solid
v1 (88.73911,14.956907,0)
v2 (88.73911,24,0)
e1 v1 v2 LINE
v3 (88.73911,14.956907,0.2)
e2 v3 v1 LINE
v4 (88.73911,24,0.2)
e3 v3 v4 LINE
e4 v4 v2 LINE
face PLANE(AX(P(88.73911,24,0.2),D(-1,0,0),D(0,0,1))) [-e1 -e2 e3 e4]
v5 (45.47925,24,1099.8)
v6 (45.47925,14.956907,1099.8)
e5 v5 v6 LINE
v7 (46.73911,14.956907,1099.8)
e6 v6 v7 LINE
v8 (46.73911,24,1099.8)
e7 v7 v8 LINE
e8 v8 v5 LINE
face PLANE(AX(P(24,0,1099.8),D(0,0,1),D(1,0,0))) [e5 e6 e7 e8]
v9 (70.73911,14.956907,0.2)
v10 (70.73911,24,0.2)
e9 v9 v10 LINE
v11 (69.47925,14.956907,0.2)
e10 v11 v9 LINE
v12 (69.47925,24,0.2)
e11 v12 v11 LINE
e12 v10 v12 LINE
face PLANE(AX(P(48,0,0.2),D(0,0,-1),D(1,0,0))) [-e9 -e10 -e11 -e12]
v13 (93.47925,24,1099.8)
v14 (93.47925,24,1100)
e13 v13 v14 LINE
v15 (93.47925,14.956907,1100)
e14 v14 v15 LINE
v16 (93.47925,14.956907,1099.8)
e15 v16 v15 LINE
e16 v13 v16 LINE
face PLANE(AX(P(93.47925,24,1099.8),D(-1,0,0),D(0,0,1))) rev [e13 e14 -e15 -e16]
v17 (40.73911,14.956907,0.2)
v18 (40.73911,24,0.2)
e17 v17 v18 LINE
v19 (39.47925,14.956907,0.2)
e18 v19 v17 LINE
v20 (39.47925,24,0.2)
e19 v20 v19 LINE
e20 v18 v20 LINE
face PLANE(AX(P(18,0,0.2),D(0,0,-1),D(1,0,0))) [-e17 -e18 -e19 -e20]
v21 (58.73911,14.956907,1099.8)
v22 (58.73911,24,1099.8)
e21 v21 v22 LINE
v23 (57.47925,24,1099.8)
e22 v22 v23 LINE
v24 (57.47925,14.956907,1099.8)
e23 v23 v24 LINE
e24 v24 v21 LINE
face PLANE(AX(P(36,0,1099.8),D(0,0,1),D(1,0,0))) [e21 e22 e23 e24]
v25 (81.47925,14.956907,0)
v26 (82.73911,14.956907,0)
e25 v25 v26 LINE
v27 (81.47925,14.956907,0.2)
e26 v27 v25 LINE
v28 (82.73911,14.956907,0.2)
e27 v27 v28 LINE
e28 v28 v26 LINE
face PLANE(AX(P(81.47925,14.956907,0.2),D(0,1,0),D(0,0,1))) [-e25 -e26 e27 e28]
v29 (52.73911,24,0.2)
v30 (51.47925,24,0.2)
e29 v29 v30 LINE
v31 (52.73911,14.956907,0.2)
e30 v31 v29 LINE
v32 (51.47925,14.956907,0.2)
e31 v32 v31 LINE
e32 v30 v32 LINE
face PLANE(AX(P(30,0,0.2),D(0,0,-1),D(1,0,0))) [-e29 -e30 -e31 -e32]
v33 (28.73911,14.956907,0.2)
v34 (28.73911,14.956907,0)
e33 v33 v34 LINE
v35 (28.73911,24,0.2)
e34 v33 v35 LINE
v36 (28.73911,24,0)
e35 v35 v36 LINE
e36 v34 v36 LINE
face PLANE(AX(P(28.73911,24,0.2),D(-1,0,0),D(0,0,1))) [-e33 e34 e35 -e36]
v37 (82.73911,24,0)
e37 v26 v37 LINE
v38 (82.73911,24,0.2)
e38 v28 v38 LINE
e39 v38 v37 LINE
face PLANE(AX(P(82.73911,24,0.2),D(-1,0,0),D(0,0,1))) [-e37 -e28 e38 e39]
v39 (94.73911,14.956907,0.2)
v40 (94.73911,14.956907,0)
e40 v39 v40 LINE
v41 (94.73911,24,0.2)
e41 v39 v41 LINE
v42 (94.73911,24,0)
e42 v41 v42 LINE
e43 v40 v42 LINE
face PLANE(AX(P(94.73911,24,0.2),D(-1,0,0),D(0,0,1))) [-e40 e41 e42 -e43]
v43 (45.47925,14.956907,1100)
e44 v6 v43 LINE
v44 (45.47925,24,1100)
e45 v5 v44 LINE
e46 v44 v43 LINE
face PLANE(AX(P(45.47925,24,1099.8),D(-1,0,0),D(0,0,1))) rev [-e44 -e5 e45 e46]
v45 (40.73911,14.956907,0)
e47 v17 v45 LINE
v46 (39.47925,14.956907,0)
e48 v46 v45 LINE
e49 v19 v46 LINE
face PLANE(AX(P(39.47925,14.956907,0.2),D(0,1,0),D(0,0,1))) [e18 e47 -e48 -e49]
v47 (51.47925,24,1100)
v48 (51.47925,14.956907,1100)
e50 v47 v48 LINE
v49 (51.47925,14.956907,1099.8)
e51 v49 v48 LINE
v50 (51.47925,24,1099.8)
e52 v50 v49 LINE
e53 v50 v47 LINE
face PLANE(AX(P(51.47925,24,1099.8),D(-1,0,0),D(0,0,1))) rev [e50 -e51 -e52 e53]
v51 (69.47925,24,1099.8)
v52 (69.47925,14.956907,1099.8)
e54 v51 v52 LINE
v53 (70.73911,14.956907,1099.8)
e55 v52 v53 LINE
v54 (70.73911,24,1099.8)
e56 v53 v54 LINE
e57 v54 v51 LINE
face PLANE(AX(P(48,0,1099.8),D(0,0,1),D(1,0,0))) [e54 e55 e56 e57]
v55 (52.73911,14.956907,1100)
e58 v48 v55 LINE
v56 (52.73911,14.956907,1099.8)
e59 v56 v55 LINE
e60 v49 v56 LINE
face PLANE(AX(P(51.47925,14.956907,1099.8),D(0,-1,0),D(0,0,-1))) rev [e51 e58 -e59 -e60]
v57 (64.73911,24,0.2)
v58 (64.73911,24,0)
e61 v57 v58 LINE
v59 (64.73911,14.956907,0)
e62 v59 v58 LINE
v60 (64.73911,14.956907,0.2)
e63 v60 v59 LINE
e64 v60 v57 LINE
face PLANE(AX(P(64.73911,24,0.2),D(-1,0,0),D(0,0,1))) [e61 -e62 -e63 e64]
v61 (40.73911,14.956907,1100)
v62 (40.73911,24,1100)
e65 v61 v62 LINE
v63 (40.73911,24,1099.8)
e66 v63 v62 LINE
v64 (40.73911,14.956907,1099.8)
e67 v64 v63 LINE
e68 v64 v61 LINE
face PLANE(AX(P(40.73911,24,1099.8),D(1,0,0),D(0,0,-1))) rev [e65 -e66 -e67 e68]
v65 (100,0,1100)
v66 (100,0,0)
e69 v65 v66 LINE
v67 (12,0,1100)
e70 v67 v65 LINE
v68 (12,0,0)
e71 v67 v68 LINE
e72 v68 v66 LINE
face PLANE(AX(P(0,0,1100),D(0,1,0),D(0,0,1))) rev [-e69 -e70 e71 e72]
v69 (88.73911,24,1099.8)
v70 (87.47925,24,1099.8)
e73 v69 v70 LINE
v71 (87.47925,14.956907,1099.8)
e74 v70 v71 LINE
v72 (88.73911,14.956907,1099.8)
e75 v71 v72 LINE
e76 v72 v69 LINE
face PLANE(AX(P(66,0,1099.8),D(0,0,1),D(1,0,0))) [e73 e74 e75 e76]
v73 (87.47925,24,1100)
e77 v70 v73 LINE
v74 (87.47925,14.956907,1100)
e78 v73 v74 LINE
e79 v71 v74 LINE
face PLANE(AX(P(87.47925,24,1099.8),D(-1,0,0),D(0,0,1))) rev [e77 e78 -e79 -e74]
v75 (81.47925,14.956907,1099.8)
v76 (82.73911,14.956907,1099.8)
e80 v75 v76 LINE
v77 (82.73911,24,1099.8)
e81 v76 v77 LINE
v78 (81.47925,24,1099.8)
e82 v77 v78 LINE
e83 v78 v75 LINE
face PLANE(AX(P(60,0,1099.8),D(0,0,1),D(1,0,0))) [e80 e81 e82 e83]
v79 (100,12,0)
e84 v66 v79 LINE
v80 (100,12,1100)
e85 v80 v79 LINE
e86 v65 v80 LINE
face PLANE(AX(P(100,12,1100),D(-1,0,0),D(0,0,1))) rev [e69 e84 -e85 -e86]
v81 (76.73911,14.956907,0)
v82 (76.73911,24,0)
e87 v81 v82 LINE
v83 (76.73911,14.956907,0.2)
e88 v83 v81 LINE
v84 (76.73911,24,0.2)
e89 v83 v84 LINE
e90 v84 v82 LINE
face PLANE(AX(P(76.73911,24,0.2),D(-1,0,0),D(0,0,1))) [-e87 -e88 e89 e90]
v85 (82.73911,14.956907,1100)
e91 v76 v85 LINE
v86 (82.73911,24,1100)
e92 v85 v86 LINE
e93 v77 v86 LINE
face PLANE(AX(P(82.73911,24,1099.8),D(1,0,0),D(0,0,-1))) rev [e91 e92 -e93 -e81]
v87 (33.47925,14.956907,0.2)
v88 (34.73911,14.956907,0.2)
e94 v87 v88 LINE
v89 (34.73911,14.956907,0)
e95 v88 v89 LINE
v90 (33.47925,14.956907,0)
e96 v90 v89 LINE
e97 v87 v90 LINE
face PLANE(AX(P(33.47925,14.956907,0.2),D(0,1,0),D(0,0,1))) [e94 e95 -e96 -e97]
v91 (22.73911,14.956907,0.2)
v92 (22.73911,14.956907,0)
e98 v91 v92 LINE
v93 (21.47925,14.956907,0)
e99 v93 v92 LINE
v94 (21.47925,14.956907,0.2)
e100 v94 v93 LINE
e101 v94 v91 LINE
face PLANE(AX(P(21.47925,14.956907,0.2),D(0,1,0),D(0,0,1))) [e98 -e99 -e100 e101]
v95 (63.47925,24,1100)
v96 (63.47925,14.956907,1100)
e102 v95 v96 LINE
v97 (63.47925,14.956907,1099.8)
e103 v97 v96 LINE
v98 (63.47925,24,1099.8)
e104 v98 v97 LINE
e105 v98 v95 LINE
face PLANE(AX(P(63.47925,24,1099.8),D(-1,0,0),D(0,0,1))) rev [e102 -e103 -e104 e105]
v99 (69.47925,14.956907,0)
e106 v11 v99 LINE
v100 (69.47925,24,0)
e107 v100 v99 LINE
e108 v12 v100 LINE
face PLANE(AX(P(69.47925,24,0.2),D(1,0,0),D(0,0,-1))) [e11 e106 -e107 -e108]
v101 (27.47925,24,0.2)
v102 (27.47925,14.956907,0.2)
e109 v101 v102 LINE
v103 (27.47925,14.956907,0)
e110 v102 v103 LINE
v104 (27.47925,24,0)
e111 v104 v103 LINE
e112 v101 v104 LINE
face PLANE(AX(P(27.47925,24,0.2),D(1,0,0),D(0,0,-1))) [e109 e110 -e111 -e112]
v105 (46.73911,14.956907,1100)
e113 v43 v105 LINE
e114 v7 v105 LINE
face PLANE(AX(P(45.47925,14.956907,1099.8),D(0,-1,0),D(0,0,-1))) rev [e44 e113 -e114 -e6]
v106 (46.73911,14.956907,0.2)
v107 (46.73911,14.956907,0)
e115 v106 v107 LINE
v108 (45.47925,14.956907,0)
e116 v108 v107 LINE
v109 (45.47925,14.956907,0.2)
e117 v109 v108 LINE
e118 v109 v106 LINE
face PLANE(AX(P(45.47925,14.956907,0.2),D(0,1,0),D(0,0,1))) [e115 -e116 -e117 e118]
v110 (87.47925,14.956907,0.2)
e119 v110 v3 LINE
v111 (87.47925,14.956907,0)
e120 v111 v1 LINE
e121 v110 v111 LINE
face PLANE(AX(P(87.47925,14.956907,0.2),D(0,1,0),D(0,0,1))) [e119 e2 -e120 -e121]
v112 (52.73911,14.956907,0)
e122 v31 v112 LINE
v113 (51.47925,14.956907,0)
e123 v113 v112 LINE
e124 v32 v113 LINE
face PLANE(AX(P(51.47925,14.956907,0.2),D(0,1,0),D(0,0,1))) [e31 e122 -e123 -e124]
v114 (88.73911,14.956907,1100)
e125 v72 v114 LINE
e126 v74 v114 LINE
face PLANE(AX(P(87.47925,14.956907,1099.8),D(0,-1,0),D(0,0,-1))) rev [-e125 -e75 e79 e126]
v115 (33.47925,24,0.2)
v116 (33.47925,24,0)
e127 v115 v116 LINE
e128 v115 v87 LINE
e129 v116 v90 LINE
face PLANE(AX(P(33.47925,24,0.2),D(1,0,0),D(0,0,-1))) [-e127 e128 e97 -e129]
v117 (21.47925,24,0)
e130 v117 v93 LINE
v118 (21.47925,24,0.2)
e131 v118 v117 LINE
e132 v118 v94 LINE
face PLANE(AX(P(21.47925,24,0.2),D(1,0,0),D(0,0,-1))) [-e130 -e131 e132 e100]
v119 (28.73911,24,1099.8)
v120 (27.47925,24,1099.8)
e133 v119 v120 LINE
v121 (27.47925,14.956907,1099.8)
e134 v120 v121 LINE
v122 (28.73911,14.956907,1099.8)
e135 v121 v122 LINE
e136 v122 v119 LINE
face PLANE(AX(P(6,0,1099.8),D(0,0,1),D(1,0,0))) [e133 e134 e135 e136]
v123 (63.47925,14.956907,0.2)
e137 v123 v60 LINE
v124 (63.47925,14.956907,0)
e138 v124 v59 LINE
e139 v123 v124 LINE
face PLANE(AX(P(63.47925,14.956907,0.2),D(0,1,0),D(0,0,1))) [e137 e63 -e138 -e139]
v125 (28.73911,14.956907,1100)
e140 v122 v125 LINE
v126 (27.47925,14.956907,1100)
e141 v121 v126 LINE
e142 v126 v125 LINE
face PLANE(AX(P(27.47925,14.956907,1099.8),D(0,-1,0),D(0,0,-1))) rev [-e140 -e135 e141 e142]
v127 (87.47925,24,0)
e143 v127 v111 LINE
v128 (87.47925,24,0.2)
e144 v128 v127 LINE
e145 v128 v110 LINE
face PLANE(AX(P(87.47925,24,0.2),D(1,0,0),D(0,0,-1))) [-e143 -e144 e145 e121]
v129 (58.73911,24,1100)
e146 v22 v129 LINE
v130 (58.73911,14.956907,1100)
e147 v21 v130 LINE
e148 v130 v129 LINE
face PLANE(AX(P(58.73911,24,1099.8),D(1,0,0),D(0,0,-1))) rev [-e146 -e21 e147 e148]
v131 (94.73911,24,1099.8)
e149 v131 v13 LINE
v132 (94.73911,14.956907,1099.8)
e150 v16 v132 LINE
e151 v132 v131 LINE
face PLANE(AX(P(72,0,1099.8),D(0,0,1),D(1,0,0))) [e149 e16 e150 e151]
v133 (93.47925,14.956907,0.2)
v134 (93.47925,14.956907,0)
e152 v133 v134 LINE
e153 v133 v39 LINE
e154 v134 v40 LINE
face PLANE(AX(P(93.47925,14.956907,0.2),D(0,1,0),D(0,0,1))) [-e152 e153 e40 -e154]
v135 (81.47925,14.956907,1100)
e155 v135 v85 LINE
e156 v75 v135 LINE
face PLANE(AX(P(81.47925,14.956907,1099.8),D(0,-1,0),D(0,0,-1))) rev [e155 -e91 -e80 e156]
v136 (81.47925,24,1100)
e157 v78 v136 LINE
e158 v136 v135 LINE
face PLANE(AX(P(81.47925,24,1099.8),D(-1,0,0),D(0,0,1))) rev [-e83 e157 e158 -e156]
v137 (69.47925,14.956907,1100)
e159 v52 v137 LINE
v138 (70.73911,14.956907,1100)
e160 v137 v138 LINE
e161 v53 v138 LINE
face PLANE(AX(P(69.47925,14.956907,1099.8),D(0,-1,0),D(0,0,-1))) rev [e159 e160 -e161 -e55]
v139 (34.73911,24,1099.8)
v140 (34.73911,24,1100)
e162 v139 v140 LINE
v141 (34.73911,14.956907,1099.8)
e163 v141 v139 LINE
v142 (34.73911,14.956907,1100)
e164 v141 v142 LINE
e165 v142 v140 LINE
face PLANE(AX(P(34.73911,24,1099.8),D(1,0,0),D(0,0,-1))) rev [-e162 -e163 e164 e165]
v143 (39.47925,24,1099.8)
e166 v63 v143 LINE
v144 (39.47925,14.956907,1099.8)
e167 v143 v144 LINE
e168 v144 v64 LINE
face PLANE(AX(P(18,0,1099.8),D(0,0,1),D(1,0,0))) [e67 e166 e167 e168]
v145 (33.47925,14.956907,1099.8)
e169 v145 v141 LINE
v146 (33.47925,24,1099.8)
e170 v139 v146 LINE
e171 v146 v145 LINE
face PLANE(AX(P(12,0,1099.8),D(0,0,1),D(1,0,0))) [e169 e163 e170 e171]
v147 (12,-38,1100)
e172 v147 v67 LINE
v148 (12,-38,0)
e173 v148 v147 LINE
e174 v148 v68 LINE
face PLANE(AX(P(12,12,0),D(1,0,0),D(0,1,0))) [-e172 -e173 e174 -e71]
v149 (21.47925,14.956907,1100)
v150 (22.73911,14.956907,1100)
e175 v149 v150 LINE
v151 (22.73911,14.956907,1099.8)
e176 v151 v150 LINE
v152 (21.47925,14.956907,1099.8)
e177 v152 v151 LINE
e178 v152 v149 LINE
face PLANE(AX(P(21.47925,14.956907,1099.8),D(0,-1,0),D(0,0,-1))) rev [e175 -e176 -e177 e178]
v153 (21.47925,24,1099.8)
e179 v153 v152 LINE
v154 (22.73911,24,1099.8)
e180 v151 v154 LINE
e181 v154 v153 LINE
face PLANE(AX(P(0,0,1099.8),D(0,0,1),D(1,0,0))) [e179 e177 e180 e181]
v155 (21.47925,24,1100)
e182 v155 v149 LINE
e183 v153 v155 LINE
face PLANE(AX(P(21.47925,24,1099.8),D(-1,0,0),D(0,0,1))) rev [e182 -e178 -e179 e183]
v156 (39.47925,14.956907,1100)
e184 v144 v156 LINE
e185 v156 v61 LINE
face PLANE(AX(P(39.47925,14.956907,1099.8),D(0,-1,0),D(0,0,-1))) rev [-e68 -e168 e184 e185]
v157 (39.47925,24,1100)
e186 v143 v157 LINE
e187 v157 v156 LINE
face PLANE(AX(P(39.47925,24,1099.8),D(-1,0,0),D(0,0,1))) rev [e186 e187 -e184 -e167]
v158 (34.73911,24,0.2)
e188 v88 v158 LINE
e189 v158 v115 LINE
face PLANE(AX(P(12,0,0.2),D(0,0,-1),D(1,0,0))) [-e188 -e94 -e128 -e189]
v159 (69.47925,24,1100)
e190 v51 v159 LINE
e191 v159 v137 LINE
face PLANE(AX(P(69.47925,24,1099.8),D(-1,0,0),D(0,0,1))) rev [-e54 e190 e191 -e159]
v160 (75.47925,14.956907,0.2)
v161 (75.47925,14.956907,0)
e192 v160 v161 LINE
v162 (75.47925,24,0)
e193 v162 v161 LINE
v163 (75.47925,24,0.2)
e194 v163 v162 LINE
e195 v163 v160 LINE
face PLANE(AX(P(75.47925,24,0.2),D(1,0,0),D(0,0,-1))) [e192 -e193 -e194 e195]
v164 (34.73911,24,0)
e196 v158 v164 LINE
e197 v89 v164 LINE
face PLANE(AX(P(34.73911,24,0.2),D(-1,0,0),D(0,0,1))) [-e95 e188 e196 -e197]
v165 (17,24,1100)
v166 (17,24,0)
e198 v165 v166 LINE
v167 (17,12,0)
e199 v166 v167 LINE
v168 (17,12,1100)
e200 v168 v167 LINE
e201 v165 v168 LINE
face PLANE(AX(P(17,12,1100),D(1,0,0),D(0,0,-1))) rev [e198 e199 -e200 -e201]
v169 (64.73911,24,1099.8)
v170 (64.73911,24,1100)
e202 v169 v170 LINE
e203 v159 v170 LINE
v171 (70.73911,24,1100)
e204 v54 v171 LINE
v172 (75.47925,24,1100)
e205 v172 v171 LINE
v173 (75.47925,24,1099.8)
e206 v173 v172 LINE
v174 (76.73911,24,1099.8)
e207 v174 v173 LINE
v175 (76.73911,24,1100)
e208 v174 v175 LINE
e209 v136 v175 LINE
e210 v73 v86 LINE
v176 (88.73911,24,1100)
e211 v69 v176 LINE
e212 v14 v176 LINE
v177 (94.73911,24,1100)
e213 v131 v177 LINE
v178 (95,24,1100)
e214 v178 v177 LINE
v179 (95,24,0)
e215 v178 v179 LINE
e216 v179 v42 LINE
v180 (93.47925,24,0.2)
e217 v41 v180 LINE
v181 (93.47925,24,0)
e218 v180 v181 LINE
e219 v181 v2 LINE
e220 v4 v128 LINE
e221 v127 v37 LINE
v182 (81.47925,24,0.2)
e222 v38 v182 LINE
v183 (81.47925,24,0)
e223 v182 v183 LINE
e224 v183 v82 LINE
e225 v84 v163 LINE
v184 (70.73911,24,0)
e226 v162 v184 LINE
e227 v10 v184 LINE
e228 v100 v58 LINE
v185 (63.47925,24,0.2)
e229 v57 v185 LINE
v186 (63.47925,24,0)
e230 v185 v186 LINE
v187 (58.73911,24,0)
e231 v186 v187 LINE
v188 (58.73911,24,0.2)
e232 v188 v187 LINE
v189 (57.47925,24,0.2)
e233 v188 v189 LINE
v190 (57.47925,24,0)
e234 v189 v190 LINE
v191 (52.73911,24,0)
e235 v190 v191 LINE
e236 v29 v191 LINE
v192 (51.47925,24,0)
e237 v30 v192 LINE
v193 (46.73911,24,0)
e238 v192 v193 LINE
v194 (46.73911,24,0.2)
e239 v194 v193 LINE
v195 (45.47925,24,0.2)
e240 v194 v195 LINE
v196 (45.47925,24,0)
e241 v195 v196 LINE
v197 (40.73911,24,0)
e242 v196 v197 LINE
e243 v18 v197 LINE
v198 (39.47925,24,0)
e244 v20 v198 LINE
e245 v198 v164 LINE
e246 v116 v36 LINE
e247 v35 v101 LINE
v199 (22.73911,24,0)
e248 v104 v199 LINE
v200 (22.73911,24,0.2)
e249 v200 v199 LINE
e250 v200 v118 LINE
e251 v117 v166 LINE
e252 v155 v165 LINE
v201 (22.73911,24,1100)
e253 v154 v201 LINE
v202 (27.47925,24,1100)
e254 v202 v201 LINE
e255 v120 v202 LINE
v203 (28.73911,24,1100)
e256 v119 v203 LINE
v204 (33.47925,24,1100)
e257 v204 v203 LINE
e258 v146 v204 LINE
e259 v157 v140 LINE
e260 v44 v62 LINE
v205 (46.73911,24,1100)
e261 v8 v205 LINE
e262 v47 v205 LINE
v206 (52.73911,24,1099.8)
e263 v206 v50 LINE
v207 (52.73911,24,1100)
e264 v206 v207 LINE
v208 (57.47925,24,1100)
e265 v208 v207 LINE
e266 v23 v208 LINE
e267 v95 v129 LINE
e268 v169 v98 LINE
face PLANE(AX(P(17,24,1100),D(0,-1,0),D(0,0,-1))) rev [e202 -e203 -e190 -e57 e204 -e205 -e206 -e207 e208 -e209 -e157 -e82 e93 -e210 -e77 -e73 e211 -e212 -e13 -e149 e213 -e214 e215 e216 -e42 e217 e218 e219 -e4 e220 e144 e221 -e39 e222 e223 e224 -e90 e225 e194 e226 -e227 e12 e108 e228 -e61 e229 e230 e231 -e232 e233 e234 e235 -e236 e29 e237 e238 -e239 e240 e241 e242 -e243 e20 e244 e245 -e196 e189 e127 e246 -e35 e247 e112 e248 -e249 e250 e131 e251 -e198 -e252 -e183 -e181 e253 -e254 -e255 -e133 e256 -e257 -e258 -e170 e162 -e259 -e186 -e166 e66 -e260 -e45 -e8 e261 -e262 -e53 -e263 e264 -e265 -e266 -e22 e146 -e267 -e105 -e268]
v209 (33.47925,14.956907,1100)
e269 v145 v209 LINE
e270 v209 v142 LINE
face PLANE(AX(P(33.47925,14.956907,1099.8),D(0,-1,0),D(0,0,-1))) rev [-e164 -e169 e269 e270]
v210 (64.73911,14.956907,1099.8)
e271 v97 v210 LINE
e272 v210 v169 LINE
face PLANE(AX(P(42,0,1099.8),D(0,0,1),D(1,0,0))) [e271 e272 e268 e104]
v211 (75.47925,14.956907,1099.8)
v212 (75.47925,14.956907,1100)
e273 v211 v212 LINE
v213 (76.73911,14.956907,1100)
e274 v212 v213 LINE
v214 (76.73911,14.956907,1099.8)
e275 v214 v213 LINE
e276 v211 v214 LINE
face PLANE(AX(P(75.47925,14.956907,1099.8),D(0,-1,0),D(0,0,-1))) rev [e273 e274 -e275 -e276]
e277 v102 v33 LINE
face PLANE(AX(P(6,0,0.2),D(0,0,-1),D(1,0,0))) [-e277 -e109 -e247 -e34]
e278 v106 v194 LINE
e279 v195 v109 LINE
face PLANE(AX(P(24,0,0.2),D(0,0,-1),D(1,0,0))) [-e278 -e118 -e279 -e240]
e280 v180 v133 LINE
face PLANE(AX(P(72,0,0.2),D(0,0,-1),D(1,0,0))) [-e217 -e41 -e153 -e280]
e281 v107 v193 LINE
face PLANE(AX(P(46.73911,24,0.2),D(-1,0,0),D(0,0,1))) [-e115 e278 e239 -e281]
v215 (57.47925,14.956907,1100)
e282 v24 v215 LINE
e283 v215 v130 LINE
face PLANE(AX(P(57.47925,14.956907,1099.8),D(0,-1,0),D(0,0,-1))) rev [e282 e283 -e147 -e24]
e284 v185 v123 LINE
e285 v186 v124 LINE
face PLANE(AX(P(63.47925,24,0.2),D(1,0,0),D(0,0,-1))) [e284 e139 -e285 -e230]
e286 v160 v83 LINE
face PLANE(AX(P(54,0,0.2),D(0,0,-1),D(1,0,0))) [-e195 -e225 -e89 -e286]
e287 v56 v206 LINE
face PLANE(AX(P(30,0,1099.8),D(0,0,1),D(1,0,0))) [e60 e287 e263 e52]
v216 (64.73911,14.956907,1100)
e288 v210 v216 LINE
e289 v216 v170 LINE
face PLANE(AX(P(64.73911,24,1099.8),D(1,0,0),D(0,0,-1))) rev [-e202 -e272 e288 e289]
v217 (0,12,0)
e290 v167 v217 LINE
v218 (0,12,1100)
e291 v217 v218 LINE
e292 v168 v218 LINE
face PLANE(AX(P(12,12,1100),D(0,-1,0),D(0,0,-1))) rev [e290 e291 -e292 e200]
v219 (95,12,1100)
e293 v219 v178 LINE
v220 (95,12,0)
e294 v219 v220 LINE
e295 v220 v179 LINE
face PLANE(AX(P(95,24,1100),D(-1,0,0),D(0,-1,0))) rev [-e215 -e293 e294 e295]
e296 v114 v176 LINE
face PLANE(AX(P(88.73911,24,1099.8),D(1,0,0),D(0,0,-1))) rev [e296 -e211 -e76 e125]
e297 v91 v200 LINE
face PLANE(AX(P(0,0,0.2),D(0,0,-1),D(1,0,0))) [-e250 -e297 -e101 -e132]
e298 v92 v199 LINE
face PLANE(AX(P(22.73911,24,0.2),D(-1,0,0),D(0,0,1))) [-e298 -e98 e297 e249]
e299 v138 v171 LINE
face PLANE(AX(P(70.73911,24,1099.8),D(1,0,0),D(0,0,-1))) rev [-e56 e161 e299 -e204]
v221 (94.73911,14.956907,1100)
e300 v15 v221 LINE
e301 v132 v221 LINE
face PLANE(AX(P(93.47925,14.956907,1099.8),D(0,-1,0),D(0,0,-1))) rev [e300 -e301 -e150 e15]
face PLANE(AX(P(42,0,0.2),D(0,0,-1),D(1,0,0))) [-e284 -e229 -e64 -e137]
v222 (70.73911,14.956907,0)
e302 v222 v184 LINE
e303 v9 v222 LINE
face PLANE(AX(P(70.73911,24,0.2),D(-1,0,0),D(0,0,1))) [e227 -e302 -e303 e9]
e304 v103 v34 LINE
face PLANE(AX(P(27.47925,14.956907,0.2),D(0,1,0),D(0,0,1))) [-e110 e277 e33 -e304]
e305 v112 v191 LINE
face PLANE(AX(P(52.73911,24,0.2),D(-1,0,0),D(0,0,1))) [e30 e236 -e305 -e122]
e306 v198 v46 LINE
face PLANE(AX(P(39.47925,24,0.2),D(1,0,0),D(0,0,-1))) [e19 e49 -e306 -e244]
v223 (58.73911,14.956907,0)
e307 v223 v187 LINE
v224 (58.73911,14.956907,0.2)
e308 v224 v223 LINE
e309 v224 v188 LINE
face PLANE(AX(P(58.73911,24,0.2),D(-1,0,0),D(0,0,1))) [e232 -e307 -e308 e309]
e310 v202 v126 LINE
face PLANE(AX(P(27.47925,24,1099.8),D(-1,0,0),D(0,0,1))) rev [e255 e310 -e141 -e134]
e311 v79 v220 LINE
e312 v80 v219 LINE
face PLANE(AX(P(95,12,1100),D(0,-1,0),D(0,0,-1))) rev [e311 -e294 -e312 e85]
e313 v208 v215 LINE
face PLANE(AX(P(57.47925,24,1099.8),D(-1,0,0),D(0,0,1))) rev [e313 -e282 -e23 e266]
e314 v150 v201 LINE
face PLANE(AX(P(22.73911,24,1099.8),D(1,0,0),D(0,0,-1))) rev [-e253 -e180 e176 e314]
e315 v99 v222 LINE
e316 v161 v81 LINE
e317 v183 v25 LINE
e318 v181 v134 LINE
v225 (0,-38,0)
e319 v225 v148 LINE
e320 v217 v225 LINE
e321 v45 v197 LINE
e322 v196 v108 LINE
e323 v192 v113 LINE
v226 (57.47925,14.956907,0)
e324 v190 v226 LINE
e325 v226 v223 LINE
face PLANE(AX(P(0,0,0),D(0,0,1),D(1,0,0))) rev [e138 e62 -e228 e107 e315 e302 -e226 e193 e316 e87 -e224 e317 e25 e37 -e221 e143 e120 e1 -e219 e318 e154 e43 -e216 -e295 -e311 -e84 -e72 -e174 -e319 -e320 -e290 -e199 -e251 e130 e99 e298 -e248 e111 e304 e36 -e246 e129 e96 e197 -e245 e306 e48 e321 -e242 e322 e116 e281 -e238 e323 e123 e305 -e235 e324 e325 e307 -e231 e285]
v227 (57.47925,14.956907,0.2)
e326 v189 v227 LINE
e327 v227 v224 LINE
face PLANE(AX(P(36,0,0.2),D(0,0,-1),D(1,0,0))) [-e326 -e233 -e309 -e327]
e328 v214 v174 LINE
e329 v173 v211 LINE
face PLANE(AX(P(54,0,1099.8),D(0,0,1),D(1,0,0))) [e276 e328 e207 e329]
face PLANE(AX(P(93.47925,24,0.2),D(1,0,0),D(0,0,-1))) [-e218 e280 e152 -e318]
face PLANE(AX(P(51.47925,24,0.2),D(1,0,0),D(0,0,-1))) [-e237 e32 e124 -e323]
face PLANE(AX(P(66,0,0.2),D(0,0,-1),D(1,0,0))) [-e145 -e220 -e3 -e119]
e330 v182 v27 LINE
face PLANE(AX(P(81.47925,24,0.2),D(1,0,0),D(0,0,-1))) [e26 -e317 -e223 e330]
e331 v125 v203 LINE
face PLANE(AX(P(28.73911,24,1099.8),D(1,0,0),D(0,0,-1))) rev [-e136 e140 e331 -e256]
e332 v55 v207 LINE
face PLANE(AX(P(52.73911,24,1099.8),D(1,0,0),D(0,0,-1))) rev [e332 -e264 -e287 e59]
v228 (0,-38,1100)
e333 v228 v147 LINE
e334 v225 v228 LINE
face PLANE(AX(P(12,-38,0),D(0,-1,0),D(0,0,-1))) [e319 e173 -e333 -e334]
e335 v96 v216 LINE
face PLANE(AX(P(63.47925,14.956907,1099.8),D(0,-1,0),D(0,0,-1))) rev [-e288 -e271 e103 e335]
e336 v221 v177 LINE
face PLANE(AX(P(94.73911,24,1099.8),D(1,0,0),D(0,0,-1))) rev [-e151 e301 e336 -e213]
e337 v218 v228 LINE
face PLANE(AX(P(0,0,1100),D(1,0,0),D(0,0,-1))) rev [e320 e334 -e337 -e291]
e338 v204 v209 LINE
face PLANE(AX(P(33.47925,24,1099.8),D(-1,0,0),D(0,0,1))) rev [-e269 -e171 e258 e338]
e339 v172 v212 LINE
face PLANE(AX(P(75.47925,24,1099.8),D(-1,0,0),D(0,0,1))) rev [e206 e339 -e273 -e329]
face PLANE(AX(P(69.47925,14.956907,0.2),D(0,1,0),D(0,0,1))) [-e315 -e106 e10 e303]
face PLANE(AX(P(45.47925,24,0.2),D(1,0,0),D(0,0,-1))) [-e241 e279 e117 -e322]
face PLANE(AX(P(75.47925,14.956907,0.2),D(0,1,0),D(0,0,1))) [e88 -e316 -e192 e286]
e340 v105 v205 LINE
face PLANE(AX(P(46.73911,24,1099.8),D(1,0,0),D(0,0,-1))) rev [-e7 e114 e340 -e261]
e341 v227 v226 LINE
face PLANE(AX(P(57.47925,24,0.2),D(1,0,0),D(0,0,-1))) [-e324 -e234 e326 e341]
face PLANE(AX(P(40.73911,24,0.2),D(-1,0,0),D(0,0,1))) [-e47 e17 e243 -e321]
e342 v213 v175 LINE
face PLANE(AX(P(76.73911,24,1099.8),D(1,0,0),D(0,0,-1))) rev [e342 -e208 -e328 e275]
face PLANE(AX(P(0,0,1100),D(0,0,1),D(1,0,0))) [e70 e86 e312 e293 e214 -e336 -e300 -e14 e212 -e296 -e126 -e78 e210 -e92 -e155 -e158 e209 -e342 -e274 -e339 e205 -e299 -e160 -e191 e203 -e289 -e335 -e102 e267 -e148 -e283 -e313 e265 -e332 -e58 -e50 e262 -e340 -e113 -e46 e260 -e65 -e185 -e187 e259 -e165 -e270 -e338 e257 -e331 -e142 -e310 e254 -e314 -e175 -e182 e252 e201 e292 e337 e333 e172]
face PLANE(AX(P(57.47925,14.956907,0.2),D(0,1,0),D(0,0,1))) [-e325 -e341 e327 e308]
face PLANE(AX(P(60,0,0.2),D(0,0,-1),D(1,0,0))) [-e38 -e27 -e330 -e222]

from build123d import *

# Parameters (mm, degrees)
BOSS_EXTRUDE1_DEPTH      = 1100
SKETCH2_W                = 1.259860676
SKETCH2_H                = 9.043092937
CUT_EXTRUDE1_DEPTH       = 0.2
LPATTERN1_COUNT          = 16
LPATTERN1_PITCH          = 6
MIRROR1_COPY_1_SKETCH_W  = 1.259860676
MIRROR1_COPY_1_SKETCH_H  = 9.043092937
MIRROR1_COPY_1_DEPTH     = 0.2
MIRROR1_COPY_2_SKETCH_W  = 1.259860676
MIRROR1_COPY_2_SKETCH_H  = 9.043092937
MIRROR1_COPY_2_DEPTH     = 0.2
MIRROR1_COPY_3_SKETCH_W  = 1.259860676
MIRROR1_COPY_3_SKETCH_H  = 9.043092937
MIRROR1_COPY_3_DEPTH     = 0.2
MIRROR1_COPY_4_SKETCH_W  = 1.259860676
MIRROR1_COPY_4_SKETCH_H  = 9.043092937
MIRROR1_COPY_4_DEPTH     = 0.2
MIRROR1_COPY_5_SKETCH_W  = 1.259860676
MIRROR1_COPY_5_SKETCH_H  = 9.043092937
MIRROR1_COPY_5_DEPTH     = 0.2
MIRROR1_COPY_6_SKETCH_W  = 1.259860676
MIRROR1_COPY_6_SKETCH_H  = 9.043092937
MIRROR1_COPY_6_DEPTH     = 0.2
MIRROR1_COPY_7_SKETCH_W  = 1.259860676
MIRROR1_COPY_7_SKETCH_H  = 9.043092937
MIRROR1_COPY_7_DEPTH     = 0.2
MIRROR1_COPY_8_SKETCH_W  = 1.259860676
MIRROR1_COPY_8_SKETCH_H  = 9.043092937
MIRROR1_COPY_8_DEPTH     = 0.2
MIRROR1_COPY_9_SKETCH_W  = 1.259860676
MIRROR1_COPY_9_SKETCH_H  = 9.043092937
MIRROR1_COPY_9_DEPTH     = 0.2
MIRROR1_COPY_10_SKETCH_W = 1.259860676
MIRROR1_COPY_10_SKETCH_H = 9.043092937
MIRROR1_COPY_10_DEPTH    = 0.2
MIRROR1_COPY_11_SKETCH_W = 1.259860676
MIRROR1_COPY_11_SKETCH_H = 9.043092937
MIRROR1_COPY_11_DEPTH    = 0.2
MIRROR1_COPY_12_SKETCH_W = 1.259860676
MIRROR1_COPY_12_SKETCH_H = 9.043092937
MIRROR1_COPY_12_DEPTH    = 0.2
MIRROR1_COPY_13_SKETCH_W = 1.259860676
MIRROR1_COPY_13_SKETCH_H = 9.043092937
MIRROR1_COPY_13_DEPTH    = 0.2
MIRROR1_COPY_14_SKETCH_W = 1.259860676
MIRROR1_COPY_14_SKETCH_H = 9.043092937
MIRROR1_COPY_14_DEPTH    = 0.2
MIRROR1_COPY_15_SKETCH_W = 1.259860676
MIRROR1_COPY_15_SKETCH_H = 9.043092937
MIRROR1_COPY_15_DEPTH    = 0.2
SKETCH3_W                = 12
SKETCH3_H                = 50
BOSS_EXTRUDE2_DEPTH      = 1100
SKETCH4_W                = 12
SKETCH4_H                = 88
CUT_EXTRUDE2_DEPTH       = 1110.053650641


with BuildPart() as part:
    # Sketch1 → Boss-Extrude1 (new body)
    with BuildSketch(Plane.XY):
        Polygon((0, 0), (100, 0), (100, 12), (95, 12), (95, 24), (17, 24), (17, 12), (12, 12), (12, 100), (0, 100), align=None)
    extrude(amount=BOSS_EXTRUDE1_DEPTH)

    # Sketch2 → Cut-Extrude1 (cut)
    with BuildSketch(Plane.XY.offset(1100)):
        with Locations((22.109179897, 19.478453532)):
            Rectangle(SKETCH2_W, SKETCH2_H)
    cut_extrude1 = extrude(amount=-CUT_EXTRUDE1_DEPTH, mode=Mode.SUBTRACT)

    # LPattern1: Cut-Extrude1 ×16
    with Locations(*[(i * LPATTERN1_PITCH, 0, 0) for i in range(1, LPATTERN1_COUNT)]):
        add(cut_extrude1, mode=Mode.SUBTRACT)

    # Mirror1: Cut-Extrude1 across plane
    add(cut_extrude1.mirror(Plane(origin=(0, 0, 550), x_dir=(1, 0, 0), z_dir=(0, 0, -1))), mode=Mode.SUBTRACT)

    # Mirror1 copy 1 sketch → Mirror1 copy 1 (cut)
    with BuildSketch(Plane(origin=(6, 0, 0), x_dir=(1, 0, 0), z_dir=(0, 0, -1))):
        with Locations((22.109179897, -19.478453532)):
            Rectangle(MIRROR1_COPY_1_SKETCH_W, MIRROR1_COPY_1_SKETCH_H)
    extrude(amount=-MIRROR1_COPY_1_DEPTH, mode=Mode.SUBTRACT)

    # Mirror1 copy 2 sketch → Mirror1 copy 2 (cut)
    with BuildSketch(Plane(origin=(12, 0, 0), x_dir=(1, 0, 0), z_dir=(0, 0, -1))):
        with Locations((22.109179897, -19.478453532)):
            Rectangle(MIRROR1_COPY_2_SKETCH_W, MIRROR1_COPY_2_SKETCH_H)
    extrude(amount=-MIRROR1_COPY_2_DEPTH, mode=Mode.SUBTRACT)

    # Mirror1 copy 3 sketch → Mirror1 copy 3 (cut)
    with BuildSketch(Plane(origin=(18, 0, 0), x_dir=(1, 0, 0), z_dir=(0, 0, -1))):
        with Locations((22.109179897, -19.478453532)):
            Rectangle(MIRROR1_COPY_3_SKETCH_W, MIRROR1_COPY_3_SKETCH_H)
    extrude(amount=-MIRROR1_COPY_3_DEPTH, mode=Mode.SUBTRACT)

    # Mirror1 copy 4 sketch → Mirror1 copy 4 (cut)
    with BuildSketch(Plane(origin=(24, 0, 0), x_dir=(1, 0, 0), z_dir=(0, 0, -1))):
        with Locations((22.109179897, -19.478453532)):
            Rectangle(MIRROR1_COPY_4_SKETCH_W, MIRROR1_COPY_4_SKETCH_H)
    extrude(amount=-MIRROR1_COPY_4_DEPTH, mode=Mode.SUBTRACT)

    # Mirror1 copy 5 sketch → Mirror1 copy 5 (cut)
    with BuildSketch(Plane(origin=(30, 0, 0), x_dir=(1, 0, 0), z_dir=(0, 0, -1))):
        with Locations((22.109179897, -19.478453532)):
            Rectangle(MIRROR1_COPY_5_SKETCH_W, MIRROR1_COPY_5_SKETCH_H)
    extrude(amount=-MIRROR1_COPY_5_DEPTH, mode=Mode.SUBTRACT)

    # Mirror1 copy 6 sketch → Mirror1 copy 6 (cut)
    with BuildSketch(Plane(origin=(36, 0, 0), x_dir=(1, 0, 0), z_dir=(0, 0, -1))):
        with Locations((22.109179897, -19.478453532)):
            Rectangle(MIRROR1_COPY_6_SKETCH_W, MIRROR1_COPY_6_SKETCH_H)
    extrude(amount=-MIRROR1_COPY_6_DEPTH, mode=Mode.SUBTRACT)

    # Mirror1 copy 7 sketch → Mirror1 copy 7 (cut)
    with BuildSketch(Plane(origin=(42, 0, 0), x_dir=(1, 0, 0), z_dir=(0, 0, -1))):
        with Locations((22.109179897, -19.478453532)):
            Rectangle(MIRROR1_COPY_7_SKETCH_W, MIRROR1_COPY_7_SKETCH_H)
    extrude(amount=-MIRROR1_COPY_7_DEPTH, mode=Mode.SUBTRACT)

    # Mirror1 copy 8 sketch → Mirror1 copy 8 (cut)
    with BuildSketch(Plane(origin=(48, 0, 0), x_dir=(1, 0, 0), z_dir=(0, 0, -1))):
        with Locations((22.109179897, -19.478453532)):
            Rectangle(MIRROR1_COPY_8_SKETCH_W, MIRROR1_COPY_8_SKETCH_H)
    extrude(amount=-MIRROR1_COPY_8_DEPTH, mode=Mode.SUBTRACT)

    # Mirror1 copy 9 sketch → Mirror1 copy 9 (cut)
    with BuildSketch(Plane(origin=(54, 0, 0), x_dir=(1, 0, 0), z_dir=(0, 0, -1))):
        with Locations((22.109179897, -19.478453532)):
            Rectangle(MIRROR1_COPY_9_SKETCH_W, MIRROR1_COPY_9_SKETCH_H)
    extrude(amount=-MIRROR1_COPY_9_DEPTH, mode=Mode.SUBTRACT)

    # Mirror1 copy 10 sketch → Mirror1 copy 10 (cut)
    with BuildSketch(Plane(origin=(60, 0, 0), x_dir=(1, 0, 0), z_dir=(0, 0, -1))):
        with Locations((22.109179897, -19.478453532)):
            Rectangle(MIRROR1_COPY_10_SKETCH_W, MIRROR1_COPY_10_SKETCH_H)
    extrude(amount=-MIRROR1_COPY_10_DEPTH, mode=Mode.SUBTRACT)

    # Mirror1 copy 11 sketch → Mirror1 copy 11 (cut)
    with BuildSketch(Plane(origin=(66, 0, 0), x_dir=(1, 0, 0), z_dir=(0, 0, -1))):
        with Locations((22.109179897, -19.478453532)):
            Rectangle(MIRROR1_COPY_11_SKETCH_W, MIRROR1_COPY_11_SKETCH_H)
    extrude(amount=-MIRROR1_COPY_11_DEPTH, mode=Mode.SUBTRACT)

    # Mirror1 copy 12 sketch → Mirror1 copy 12 (cut)
    with BuildSketch(Plane(origin=(72, 0, 0), x_dir=(1, 0, 0), z_dir=(0, 0, -1))):
        with Locations((22.109179897, -19.478453532)):
            Rectangle(MIRROR1_COPY_12_SKETCH_W, MIRROR1_COPY_12_SKETCH_H)
    extrude(amount=-MIRROR1_COPY_12_DEPTH, mode=Mode.SUBTRACT)

    # Mirror1 copy 13 sketch → Mirror1 copy 13 (cut)
    with BuildSketch(Plane(origin=(78, 0, 0), x_dir=(1, 0, 0), z_dir=(0, 0, -1))):
        with Locations((22.109179897, -19.478453532)):
            Rectangle(MIRROR1_COPY_13_SKETCH_W, MIRROR1_COPY_13_SKETCH_H)
    extrude(amount=-MIRROR1_COPY_13_DEPTH, mode=Mode.SUBTRACT)

    # Mirror1 copy 14 sketch → Mirror1 copy 14 (cut)
    with BuildSketch(Plane(origin=(84, 0, 0), x_dir=(1, 0, 0), z_dir=(0, 0, -1))):
        with Locations((22.109179897, -19.478453532)):
            Rectangle(MIRROR1_COPY_14_SKETCH_W, MIRROR1_COPY_14_SKETCH_H)
    extrude(amount=-MIRROR1_COPY_14_DEPTH, mode=Mode.SUBTRACT)

    # Mirror1 copy 15 sketch → Mirror1 copy 15 (cut)
    with BuildSketch(Plane(origin=(90, 0, 0), x_dir=(1, 0, 0), z_dir=(0, 0, -1))):
        with Locations((22.109179897, -19.478453532)):
            Rectangle(MIRROR1_COPY_15_SKETCH_W, MIRROR1_COPY_15_SKETCH_H)
    extrude(amount=-MIRROR1_COPY_15_DEPTH, mode=Mode.SUBTRACT)

    # Sketch3 → Boss-Extrude2 (add)
    with BuildSketch(Plane.XY.offset(1100)):
        with Locations((6, -13)):
            Rectangle(SKETCH3_W, SKETCH3_H)
    extrude(amount=-BOSS_EXTRUDE2_DEPTH)

    # Sketch4 → Cut-Extrude2 (cut, through all)
    with BuildSketch(Plane.XY.offset(1100)):
        with Locations((6, 56)):
            Rectangle(SKETCH4_W, SKETCH4_H)
    extrude(amount=-CUT_EXTRUDE2_DEPTH, mode=Mode.SUBTRACT)


solid = part.part
